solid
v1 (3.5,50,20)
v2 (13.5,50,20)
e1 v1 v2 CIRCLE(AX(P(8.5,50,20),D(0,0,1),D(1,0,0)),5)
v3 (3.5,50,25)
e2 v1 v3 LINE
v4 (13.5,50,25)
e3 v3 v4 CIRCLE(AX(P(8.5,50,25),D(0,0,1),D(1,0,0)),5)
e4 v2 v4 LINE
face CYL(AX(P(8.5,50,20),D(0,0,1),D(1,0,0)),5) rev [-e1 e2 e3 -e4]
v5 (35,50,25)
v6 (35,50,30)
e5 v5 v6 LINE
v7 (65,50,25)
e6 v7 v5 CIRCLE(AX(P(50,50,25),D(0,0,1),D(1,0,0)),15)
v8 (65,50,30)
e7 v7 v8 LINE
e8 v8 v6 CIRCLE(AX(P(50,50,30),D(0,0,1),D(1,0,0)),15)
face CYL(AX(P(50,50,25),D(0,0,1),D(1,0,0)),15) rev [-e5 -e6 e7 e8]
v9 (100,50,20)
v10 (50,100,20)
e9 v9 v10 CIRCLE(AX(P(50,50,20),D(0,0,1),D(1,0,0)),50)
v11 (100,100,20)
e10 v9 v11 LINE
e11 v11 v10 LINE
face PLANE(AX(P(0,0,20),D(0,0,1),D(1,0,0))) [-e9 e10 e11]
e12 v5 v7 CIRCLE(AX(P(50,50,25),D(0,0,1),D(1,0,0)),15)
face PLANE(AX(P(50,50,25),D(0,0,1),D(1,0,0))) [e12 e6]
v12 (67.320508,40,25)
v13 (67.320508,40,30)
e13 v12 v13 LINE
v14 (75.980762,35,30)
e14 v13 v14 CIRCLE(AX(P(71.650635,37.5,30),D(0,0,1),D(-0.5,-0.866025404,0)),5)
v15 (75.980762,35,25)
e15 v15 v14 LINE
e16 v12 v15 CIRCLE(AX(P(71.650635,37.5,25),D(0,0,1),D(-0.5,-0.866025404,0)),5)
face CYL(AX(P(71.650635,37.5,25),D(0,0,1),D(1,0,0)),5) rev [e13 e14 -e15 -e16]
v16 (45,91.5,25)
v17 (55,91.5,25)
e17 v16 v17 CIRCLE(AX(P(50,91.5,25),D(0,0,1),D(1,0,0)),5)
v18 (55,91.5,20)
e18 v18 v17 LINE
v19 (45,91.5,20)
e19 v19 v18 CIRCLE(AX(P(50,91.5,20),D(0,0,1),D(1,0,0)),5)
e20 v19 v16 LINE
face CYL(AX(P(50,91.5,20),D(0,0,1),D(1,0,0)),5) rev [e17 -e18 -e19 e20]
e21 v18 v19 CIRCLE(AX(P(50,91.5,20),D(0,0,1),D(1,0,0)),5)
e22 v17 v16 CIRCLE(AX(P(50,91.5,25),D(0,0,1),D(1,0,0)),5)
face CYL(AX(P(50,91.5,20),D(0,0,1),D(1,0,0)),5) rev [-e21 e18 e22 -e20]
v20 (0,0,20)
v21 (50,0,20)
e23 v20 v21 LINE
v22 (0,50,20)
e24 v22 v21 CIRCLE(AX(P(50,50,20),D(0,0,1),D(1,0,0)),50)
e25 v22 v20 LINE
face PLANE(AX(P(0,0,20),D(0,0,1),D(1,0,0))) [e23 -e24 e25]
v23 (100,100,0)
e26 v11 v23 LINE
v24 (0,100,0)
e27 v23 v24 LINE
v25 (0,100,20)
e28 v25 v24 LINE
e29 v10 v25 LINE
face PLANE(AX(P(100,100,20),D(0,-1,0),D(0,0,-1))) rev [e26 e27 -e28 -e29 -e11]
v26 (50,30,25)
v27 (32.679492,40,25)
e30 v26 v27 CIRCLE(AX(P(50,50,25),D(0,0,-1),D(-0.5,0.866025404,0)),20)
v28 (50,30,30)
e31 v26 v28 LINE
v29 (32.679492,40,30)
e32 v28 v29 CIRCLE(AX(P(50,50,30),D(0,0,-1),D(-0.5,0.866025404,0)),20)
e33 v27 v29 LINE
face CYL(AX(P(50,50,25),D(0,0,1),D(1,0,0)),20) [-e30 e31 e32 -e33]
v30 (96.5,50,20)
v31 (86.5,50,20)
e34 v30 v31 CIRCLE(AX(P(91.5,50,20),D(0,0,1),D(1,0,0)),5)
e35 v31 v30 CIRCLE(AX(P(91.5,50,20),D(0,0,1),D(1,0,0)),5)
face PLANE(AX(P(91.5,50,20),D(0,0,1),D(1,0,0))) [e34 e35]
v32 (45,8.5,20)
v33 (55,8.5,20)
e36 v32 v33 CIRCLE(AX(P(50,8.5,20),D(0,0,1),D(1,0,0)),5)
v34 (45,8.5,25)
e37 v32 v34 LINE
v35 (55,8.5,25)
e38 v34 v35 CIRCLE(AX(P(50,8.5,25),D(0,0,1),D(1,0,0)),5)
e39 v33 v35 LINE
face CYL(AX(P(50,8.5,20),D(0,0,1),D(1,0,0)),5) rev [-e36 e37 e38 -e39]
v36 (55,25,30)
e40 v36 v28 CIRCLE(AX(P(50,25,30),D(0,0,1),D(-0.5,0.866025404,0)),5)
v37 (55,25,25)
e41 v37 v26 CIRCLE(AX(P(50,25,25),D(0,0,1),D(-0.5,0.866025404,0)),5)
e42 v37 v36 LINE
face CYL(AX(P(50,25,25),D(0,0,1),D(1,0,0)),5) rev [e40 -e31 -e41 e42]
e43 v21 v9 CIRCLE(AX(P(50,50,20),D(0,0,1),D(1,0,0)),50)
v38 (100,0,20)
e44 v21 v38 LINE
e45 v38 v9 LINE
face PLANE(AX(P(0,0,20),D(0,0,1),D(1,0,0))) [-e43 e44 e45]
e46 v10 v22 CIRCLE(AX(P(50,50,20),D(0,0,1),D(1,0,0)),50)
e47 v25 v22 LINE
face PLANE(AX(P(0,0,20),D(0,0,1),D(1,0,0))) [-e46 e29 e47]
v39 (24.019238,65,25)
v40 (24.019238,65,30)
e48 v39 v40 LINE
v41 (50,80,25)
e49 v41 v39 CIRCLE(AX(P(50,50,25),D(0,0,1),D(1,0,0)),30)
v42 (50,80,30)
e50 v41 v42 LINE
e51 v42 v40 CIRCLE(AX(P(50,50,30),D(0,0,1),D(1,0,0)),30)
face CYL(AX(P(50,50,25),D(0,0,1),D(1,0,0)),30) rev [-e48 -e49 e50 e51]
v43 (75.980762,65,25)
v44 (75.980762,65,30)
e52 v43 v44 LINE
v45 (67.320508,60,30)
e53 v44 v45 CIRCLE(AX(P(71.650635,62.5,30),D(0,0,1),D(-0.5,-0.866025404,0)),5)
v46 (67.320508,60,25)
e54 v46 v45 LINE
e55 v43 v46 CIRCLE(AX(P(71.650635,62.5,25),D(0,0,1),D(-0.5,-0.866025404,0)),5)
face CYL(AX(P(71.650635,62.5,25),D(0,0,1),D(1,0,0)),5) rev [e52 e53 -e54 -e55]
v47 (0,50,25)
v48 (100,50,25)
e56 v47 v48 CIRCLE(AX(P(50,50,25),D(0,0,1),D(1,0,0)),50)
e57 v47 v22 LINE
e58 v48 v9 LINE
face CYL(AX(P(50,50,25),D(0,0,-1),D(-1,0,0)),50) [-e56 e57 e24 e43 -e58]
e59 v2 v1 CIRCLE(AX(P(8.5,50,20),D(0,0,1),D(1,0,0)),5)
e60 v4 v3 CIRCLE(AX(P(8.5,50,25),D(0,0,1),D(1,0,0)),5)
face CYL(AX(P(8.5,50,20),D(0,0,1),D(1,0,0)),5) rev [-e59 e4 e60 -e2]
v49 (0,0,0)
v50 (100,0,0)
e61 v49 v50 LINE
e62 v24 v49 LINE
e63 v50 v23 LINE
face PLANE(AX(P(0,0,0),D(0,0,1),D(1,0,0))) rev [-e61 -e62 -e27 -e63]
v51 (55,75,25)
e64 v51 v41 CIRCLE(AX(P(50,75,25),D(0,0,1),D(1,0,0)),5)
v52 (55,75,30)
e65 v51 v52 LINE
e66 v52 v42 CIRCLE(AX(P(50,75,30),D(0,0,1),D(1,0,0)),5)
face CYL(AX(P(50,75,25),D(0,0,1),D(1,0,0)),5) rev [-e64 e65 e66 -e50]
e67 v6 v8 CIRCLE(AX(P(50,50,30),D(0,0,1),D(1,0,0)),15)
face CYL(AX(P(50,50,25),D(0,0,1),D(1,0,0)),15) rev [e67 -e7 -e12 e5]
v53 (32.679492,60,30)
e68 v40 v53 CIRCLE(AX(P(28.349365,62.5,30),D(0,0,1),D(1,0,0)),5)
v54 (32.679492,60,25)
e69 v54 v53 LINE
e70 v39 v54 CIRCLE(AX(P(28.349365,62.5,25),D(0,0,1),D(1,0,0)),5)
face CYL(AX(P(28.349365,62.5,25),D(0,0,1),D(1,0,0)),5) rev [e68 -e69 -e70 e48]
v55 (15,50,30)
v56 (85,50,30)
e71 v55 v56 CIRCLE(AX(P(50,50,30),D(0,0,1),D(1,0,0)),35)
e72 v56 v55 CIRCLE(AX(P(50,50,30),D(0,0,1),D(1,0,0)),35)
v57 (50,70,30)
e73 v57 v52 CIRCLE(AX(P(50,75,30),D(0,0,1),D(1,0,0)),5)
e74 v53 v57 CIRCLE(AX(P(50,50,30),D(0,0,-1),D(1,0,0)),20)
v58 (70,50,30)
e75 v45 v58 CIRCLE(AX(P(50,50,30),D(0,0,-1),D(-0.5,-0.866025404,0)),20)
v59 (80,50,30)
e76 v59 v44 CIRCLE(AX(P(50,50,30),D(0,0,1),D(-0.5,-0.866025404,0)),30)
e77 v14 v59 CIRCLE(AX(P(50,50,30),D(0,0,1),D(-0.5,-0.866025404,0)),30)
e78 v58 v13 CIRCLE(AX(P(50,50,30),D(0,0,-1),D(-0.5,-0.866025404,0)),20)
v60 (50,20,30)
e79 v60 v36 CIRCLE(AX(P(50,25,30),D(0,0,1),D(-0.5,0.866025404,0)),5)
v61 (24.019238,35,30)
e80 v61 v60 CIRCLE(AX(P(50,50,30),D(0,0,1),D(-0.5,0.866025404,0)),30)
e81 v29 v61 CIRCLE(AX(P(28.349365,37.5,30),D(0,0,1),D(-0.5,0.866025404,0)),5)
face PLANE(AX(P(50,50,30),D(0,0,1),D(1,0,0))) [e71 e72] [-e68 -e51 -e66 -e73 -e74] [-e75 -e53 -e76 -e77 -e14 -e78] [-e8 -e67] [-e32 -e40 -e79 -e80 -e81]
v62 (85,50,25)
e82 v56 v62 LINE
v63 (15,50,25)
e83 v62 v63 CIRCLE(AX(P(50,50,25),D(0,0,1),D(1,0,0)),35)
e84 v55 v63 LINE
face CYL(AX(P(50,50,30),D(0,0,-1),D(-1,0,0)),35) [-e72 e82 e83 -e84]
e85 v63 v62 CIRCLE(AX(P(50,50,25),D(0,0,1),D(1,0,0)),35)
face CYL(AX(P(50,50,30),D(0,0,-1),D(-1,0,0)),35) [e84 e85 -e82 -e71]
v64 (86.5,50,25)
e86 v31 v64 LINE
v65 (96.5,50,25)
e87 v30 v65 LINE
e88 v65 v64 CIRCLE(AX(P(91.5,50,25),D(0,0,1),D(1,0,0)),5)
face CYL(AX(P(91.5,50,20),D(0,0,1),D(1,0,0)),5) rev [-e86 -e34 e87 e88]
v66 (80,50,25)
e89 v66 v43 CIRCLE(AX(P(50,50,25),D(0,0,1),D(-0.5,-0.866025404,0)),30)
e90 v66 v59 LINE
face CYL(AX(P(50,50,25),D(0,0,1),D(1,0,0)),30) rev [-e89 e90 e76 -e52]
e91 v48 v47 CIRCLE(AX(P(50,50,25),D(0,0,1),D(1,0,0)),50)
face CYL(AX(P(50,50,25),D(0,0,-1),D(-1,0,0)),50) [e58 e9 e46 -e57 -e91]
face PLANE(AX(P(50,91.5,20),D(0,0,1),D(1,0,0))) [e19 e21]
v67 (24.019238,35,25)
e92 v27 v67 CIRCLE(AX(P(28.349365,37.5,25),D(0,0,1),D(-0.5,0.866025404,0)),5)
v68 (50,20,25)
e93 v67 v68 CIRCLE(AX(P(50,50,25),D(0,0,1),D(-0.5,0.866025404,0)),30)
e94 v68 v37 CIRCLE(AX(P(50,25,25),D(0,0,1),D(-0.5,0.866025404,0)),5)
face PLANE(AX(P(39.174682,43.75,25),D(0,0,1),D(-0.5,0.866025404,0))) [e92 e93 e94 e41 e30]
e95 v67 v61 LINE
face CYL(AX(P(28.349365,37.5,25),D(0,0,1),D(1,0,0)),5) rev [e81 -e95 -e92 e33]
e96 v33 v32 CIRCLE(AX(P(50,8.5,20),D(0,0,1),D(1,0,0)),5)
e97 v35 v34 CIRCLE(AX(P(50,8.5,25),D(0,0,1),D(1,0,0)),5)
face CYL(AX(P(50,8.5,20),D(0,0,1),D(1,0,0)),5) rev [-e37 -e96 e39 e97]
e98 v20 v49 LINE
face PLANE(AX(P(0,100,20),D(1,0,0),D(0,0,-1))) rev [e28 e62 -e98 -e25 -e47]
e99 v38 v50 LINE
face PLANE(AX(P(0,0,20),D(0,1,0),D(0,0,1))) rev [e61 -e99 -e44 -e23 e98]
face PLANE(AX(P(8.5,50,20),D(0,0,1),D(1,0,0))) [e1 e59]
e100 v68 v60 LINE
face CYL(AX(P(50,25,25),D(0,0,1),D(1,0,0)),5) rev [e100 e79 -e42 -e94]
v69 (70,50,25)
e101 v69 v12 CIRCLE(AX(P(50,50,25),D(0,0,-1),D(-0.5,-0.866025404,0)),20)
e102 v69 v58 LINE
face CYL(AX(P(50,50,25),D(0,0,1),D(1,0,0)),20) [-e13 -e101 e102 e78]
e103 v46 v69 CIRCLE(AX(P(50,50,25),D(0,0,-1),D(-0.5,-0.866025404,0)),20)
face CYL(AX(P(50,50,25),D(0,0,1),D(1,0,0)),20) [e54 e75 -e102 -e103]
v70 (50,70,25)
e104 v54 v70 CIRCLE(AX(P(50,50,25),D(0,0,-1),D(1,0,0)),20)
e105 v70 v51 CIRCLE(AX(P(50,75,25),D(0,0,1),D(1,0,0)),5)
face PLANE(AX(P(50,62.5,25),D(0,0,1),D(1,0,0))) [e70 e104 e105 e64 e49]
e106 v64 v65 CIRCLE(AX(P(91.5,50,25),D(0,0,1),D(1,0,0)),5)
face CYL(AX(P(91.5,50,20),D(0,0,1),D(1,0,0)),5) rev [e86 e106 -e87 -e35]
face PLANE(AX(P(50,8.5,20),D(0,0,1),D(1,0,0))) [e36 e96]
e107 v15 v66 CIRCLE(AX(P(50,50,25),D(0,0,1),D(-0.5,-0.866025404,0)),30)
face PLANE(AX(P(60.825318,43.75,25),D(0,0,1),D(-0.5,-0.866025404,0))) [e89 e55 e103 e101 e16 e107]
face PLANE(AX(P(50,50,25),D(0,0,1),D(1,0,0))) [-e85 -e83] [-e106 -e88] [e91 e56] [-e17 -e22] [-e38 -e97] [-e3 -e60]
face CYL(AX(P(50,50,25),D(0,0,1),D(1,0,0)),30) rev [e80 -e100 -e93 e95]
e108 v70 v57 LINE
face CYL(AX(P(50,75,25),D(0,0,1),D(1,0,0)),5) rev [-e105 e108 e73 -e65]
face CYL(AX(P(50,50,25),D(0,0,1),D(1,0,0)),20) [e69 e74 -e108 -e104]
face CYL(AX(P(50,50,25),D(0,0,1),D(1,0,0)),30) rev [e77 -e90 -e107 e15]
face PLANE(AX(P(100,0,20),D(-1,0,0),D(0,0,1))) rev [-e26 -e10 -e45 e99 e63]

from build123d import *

# Parameters (mm, degrees)
BASE_PLATE_SKETCH_W         = 100
BASE_PLATE_SKETCH_H         = 100
BASE_PLATE_100X100X20_DEPTH = 20
FLANGE_SKETCH_R             = 50
FLANGE_100X5_DEPTH          = 5
FLANGE_BOLT_HOLES_SKETCH_R  = 5
FLANGE_BOLT_HOLES_4X_DEPTH  = 5
HUB_SKETCH_R                = 35
HUB_70X5_DEPTH              = 5
ARC_SLOT_DEPTH              = 5
BORE_SKETCH_R               = 15
BORE_30X5_DEPTH             = 5
ARC_SLOT_PATTERN_3X_COUNT   = 3


with BuildPart() as part:
    # Base Plate Sketch → Base Plate 100x100x20 (new body)
    with BuildSketch(Plane.XY):
        with Locations((50, 50)):
            Rectangle(BASE_PLATE_SKETCH_W, BASE_PLATE_SKETCH_H)
    extrude(amount=BASE_PLATE_100X100X20_DEPTH)

    # Flange Sketch → Flange Ø100x5 (add)
    with BuildSketch(Plane.XY.offset(20)):
        with Locations((50, 50)):
            Circle(FLANGE_SKETCH_R)
    extrude(amount=FLANGE_100X5_DEPTH)

    # Flange Bolt Holes Sketch → Flange Bolt Holes 4x (cut)
    with BuildSketch(Plane.XY.offset(25)):
        with Locations((50, 91.5)):
            Circle(FLANGE_BOLT_HOLES_SKETCH_R)
        with Locations((91.5, 50)):
            Circle(FLANGE_BOLT_HOLES_SKETCH_R)
        with Locations((50, 8.5)):
            Circle(FLANGE_BOLT_HOLES_SKETCH_R)
        with Locations((8.5, 50)):
            Circle(FLANGE_BOLT_HOLES_SKETCH_R)
    extrude(amount=-FLANGE_BOLT_HOLES_4X_DEPTH, mode=Mode.SUBTRACT)

    # Hub Sketch → Hub Ø70x5 (add)
    with BuildSketch(Plane.XY.offset(25)):
        with Locations((50, 50)):
            Circle(HUB_SKETCH_R)
    extrude(amount=HUB_70X5_DEPTH)

    # Arc Slot Sketch → Arc Slot (cut)
    with BuildSketch(Plane.XY.offset(30)):
        with BuildLine():
            ThreePointArc((50, 70), (40, 67.320508076), (32.679491924, 60))
            ThreePointArc((32.679491924, 60), (25.849364905, 58.169872981), (24.019237886, 65))
            ThreePointArc((24.019237886, 65), (35, 75.980762114), (50, 80))
            ThreePointArc((50, 80), (55, 75), (50, 70))
        make_face()
    arc_slot = extrude(amount=-ARC_SLOT_DEPTH, mode=Mode.SUBTRACT)

    # Bore Sketch → Bore Ø30x5 (cut)
    with BuildSketch(Plane.XY.offset(30)):
        with Locations((50, 50)):
            Circle(BORE_SKETCH_R)
    extrude(amount=-BORE_30X5_DEPTH, mode=Mode.SUBTRACT)

    # Arc Slot Pattern 3x: Arc Slot ×3 about axis
    arc_slot_pattern_3x_axis = Axis((50, 50, 0), (0, 0, 1))
    for i in range(1, ARC_SLOT_PATTERN_3X_COUNT):
        add(arc_slot.rotate(arc_slot_pattern_3x_axis, i * 360 / ARC_SLOT_PATTERN_3X_COUNT), mode=Mode.SUBTRACT)


solid = part.part
